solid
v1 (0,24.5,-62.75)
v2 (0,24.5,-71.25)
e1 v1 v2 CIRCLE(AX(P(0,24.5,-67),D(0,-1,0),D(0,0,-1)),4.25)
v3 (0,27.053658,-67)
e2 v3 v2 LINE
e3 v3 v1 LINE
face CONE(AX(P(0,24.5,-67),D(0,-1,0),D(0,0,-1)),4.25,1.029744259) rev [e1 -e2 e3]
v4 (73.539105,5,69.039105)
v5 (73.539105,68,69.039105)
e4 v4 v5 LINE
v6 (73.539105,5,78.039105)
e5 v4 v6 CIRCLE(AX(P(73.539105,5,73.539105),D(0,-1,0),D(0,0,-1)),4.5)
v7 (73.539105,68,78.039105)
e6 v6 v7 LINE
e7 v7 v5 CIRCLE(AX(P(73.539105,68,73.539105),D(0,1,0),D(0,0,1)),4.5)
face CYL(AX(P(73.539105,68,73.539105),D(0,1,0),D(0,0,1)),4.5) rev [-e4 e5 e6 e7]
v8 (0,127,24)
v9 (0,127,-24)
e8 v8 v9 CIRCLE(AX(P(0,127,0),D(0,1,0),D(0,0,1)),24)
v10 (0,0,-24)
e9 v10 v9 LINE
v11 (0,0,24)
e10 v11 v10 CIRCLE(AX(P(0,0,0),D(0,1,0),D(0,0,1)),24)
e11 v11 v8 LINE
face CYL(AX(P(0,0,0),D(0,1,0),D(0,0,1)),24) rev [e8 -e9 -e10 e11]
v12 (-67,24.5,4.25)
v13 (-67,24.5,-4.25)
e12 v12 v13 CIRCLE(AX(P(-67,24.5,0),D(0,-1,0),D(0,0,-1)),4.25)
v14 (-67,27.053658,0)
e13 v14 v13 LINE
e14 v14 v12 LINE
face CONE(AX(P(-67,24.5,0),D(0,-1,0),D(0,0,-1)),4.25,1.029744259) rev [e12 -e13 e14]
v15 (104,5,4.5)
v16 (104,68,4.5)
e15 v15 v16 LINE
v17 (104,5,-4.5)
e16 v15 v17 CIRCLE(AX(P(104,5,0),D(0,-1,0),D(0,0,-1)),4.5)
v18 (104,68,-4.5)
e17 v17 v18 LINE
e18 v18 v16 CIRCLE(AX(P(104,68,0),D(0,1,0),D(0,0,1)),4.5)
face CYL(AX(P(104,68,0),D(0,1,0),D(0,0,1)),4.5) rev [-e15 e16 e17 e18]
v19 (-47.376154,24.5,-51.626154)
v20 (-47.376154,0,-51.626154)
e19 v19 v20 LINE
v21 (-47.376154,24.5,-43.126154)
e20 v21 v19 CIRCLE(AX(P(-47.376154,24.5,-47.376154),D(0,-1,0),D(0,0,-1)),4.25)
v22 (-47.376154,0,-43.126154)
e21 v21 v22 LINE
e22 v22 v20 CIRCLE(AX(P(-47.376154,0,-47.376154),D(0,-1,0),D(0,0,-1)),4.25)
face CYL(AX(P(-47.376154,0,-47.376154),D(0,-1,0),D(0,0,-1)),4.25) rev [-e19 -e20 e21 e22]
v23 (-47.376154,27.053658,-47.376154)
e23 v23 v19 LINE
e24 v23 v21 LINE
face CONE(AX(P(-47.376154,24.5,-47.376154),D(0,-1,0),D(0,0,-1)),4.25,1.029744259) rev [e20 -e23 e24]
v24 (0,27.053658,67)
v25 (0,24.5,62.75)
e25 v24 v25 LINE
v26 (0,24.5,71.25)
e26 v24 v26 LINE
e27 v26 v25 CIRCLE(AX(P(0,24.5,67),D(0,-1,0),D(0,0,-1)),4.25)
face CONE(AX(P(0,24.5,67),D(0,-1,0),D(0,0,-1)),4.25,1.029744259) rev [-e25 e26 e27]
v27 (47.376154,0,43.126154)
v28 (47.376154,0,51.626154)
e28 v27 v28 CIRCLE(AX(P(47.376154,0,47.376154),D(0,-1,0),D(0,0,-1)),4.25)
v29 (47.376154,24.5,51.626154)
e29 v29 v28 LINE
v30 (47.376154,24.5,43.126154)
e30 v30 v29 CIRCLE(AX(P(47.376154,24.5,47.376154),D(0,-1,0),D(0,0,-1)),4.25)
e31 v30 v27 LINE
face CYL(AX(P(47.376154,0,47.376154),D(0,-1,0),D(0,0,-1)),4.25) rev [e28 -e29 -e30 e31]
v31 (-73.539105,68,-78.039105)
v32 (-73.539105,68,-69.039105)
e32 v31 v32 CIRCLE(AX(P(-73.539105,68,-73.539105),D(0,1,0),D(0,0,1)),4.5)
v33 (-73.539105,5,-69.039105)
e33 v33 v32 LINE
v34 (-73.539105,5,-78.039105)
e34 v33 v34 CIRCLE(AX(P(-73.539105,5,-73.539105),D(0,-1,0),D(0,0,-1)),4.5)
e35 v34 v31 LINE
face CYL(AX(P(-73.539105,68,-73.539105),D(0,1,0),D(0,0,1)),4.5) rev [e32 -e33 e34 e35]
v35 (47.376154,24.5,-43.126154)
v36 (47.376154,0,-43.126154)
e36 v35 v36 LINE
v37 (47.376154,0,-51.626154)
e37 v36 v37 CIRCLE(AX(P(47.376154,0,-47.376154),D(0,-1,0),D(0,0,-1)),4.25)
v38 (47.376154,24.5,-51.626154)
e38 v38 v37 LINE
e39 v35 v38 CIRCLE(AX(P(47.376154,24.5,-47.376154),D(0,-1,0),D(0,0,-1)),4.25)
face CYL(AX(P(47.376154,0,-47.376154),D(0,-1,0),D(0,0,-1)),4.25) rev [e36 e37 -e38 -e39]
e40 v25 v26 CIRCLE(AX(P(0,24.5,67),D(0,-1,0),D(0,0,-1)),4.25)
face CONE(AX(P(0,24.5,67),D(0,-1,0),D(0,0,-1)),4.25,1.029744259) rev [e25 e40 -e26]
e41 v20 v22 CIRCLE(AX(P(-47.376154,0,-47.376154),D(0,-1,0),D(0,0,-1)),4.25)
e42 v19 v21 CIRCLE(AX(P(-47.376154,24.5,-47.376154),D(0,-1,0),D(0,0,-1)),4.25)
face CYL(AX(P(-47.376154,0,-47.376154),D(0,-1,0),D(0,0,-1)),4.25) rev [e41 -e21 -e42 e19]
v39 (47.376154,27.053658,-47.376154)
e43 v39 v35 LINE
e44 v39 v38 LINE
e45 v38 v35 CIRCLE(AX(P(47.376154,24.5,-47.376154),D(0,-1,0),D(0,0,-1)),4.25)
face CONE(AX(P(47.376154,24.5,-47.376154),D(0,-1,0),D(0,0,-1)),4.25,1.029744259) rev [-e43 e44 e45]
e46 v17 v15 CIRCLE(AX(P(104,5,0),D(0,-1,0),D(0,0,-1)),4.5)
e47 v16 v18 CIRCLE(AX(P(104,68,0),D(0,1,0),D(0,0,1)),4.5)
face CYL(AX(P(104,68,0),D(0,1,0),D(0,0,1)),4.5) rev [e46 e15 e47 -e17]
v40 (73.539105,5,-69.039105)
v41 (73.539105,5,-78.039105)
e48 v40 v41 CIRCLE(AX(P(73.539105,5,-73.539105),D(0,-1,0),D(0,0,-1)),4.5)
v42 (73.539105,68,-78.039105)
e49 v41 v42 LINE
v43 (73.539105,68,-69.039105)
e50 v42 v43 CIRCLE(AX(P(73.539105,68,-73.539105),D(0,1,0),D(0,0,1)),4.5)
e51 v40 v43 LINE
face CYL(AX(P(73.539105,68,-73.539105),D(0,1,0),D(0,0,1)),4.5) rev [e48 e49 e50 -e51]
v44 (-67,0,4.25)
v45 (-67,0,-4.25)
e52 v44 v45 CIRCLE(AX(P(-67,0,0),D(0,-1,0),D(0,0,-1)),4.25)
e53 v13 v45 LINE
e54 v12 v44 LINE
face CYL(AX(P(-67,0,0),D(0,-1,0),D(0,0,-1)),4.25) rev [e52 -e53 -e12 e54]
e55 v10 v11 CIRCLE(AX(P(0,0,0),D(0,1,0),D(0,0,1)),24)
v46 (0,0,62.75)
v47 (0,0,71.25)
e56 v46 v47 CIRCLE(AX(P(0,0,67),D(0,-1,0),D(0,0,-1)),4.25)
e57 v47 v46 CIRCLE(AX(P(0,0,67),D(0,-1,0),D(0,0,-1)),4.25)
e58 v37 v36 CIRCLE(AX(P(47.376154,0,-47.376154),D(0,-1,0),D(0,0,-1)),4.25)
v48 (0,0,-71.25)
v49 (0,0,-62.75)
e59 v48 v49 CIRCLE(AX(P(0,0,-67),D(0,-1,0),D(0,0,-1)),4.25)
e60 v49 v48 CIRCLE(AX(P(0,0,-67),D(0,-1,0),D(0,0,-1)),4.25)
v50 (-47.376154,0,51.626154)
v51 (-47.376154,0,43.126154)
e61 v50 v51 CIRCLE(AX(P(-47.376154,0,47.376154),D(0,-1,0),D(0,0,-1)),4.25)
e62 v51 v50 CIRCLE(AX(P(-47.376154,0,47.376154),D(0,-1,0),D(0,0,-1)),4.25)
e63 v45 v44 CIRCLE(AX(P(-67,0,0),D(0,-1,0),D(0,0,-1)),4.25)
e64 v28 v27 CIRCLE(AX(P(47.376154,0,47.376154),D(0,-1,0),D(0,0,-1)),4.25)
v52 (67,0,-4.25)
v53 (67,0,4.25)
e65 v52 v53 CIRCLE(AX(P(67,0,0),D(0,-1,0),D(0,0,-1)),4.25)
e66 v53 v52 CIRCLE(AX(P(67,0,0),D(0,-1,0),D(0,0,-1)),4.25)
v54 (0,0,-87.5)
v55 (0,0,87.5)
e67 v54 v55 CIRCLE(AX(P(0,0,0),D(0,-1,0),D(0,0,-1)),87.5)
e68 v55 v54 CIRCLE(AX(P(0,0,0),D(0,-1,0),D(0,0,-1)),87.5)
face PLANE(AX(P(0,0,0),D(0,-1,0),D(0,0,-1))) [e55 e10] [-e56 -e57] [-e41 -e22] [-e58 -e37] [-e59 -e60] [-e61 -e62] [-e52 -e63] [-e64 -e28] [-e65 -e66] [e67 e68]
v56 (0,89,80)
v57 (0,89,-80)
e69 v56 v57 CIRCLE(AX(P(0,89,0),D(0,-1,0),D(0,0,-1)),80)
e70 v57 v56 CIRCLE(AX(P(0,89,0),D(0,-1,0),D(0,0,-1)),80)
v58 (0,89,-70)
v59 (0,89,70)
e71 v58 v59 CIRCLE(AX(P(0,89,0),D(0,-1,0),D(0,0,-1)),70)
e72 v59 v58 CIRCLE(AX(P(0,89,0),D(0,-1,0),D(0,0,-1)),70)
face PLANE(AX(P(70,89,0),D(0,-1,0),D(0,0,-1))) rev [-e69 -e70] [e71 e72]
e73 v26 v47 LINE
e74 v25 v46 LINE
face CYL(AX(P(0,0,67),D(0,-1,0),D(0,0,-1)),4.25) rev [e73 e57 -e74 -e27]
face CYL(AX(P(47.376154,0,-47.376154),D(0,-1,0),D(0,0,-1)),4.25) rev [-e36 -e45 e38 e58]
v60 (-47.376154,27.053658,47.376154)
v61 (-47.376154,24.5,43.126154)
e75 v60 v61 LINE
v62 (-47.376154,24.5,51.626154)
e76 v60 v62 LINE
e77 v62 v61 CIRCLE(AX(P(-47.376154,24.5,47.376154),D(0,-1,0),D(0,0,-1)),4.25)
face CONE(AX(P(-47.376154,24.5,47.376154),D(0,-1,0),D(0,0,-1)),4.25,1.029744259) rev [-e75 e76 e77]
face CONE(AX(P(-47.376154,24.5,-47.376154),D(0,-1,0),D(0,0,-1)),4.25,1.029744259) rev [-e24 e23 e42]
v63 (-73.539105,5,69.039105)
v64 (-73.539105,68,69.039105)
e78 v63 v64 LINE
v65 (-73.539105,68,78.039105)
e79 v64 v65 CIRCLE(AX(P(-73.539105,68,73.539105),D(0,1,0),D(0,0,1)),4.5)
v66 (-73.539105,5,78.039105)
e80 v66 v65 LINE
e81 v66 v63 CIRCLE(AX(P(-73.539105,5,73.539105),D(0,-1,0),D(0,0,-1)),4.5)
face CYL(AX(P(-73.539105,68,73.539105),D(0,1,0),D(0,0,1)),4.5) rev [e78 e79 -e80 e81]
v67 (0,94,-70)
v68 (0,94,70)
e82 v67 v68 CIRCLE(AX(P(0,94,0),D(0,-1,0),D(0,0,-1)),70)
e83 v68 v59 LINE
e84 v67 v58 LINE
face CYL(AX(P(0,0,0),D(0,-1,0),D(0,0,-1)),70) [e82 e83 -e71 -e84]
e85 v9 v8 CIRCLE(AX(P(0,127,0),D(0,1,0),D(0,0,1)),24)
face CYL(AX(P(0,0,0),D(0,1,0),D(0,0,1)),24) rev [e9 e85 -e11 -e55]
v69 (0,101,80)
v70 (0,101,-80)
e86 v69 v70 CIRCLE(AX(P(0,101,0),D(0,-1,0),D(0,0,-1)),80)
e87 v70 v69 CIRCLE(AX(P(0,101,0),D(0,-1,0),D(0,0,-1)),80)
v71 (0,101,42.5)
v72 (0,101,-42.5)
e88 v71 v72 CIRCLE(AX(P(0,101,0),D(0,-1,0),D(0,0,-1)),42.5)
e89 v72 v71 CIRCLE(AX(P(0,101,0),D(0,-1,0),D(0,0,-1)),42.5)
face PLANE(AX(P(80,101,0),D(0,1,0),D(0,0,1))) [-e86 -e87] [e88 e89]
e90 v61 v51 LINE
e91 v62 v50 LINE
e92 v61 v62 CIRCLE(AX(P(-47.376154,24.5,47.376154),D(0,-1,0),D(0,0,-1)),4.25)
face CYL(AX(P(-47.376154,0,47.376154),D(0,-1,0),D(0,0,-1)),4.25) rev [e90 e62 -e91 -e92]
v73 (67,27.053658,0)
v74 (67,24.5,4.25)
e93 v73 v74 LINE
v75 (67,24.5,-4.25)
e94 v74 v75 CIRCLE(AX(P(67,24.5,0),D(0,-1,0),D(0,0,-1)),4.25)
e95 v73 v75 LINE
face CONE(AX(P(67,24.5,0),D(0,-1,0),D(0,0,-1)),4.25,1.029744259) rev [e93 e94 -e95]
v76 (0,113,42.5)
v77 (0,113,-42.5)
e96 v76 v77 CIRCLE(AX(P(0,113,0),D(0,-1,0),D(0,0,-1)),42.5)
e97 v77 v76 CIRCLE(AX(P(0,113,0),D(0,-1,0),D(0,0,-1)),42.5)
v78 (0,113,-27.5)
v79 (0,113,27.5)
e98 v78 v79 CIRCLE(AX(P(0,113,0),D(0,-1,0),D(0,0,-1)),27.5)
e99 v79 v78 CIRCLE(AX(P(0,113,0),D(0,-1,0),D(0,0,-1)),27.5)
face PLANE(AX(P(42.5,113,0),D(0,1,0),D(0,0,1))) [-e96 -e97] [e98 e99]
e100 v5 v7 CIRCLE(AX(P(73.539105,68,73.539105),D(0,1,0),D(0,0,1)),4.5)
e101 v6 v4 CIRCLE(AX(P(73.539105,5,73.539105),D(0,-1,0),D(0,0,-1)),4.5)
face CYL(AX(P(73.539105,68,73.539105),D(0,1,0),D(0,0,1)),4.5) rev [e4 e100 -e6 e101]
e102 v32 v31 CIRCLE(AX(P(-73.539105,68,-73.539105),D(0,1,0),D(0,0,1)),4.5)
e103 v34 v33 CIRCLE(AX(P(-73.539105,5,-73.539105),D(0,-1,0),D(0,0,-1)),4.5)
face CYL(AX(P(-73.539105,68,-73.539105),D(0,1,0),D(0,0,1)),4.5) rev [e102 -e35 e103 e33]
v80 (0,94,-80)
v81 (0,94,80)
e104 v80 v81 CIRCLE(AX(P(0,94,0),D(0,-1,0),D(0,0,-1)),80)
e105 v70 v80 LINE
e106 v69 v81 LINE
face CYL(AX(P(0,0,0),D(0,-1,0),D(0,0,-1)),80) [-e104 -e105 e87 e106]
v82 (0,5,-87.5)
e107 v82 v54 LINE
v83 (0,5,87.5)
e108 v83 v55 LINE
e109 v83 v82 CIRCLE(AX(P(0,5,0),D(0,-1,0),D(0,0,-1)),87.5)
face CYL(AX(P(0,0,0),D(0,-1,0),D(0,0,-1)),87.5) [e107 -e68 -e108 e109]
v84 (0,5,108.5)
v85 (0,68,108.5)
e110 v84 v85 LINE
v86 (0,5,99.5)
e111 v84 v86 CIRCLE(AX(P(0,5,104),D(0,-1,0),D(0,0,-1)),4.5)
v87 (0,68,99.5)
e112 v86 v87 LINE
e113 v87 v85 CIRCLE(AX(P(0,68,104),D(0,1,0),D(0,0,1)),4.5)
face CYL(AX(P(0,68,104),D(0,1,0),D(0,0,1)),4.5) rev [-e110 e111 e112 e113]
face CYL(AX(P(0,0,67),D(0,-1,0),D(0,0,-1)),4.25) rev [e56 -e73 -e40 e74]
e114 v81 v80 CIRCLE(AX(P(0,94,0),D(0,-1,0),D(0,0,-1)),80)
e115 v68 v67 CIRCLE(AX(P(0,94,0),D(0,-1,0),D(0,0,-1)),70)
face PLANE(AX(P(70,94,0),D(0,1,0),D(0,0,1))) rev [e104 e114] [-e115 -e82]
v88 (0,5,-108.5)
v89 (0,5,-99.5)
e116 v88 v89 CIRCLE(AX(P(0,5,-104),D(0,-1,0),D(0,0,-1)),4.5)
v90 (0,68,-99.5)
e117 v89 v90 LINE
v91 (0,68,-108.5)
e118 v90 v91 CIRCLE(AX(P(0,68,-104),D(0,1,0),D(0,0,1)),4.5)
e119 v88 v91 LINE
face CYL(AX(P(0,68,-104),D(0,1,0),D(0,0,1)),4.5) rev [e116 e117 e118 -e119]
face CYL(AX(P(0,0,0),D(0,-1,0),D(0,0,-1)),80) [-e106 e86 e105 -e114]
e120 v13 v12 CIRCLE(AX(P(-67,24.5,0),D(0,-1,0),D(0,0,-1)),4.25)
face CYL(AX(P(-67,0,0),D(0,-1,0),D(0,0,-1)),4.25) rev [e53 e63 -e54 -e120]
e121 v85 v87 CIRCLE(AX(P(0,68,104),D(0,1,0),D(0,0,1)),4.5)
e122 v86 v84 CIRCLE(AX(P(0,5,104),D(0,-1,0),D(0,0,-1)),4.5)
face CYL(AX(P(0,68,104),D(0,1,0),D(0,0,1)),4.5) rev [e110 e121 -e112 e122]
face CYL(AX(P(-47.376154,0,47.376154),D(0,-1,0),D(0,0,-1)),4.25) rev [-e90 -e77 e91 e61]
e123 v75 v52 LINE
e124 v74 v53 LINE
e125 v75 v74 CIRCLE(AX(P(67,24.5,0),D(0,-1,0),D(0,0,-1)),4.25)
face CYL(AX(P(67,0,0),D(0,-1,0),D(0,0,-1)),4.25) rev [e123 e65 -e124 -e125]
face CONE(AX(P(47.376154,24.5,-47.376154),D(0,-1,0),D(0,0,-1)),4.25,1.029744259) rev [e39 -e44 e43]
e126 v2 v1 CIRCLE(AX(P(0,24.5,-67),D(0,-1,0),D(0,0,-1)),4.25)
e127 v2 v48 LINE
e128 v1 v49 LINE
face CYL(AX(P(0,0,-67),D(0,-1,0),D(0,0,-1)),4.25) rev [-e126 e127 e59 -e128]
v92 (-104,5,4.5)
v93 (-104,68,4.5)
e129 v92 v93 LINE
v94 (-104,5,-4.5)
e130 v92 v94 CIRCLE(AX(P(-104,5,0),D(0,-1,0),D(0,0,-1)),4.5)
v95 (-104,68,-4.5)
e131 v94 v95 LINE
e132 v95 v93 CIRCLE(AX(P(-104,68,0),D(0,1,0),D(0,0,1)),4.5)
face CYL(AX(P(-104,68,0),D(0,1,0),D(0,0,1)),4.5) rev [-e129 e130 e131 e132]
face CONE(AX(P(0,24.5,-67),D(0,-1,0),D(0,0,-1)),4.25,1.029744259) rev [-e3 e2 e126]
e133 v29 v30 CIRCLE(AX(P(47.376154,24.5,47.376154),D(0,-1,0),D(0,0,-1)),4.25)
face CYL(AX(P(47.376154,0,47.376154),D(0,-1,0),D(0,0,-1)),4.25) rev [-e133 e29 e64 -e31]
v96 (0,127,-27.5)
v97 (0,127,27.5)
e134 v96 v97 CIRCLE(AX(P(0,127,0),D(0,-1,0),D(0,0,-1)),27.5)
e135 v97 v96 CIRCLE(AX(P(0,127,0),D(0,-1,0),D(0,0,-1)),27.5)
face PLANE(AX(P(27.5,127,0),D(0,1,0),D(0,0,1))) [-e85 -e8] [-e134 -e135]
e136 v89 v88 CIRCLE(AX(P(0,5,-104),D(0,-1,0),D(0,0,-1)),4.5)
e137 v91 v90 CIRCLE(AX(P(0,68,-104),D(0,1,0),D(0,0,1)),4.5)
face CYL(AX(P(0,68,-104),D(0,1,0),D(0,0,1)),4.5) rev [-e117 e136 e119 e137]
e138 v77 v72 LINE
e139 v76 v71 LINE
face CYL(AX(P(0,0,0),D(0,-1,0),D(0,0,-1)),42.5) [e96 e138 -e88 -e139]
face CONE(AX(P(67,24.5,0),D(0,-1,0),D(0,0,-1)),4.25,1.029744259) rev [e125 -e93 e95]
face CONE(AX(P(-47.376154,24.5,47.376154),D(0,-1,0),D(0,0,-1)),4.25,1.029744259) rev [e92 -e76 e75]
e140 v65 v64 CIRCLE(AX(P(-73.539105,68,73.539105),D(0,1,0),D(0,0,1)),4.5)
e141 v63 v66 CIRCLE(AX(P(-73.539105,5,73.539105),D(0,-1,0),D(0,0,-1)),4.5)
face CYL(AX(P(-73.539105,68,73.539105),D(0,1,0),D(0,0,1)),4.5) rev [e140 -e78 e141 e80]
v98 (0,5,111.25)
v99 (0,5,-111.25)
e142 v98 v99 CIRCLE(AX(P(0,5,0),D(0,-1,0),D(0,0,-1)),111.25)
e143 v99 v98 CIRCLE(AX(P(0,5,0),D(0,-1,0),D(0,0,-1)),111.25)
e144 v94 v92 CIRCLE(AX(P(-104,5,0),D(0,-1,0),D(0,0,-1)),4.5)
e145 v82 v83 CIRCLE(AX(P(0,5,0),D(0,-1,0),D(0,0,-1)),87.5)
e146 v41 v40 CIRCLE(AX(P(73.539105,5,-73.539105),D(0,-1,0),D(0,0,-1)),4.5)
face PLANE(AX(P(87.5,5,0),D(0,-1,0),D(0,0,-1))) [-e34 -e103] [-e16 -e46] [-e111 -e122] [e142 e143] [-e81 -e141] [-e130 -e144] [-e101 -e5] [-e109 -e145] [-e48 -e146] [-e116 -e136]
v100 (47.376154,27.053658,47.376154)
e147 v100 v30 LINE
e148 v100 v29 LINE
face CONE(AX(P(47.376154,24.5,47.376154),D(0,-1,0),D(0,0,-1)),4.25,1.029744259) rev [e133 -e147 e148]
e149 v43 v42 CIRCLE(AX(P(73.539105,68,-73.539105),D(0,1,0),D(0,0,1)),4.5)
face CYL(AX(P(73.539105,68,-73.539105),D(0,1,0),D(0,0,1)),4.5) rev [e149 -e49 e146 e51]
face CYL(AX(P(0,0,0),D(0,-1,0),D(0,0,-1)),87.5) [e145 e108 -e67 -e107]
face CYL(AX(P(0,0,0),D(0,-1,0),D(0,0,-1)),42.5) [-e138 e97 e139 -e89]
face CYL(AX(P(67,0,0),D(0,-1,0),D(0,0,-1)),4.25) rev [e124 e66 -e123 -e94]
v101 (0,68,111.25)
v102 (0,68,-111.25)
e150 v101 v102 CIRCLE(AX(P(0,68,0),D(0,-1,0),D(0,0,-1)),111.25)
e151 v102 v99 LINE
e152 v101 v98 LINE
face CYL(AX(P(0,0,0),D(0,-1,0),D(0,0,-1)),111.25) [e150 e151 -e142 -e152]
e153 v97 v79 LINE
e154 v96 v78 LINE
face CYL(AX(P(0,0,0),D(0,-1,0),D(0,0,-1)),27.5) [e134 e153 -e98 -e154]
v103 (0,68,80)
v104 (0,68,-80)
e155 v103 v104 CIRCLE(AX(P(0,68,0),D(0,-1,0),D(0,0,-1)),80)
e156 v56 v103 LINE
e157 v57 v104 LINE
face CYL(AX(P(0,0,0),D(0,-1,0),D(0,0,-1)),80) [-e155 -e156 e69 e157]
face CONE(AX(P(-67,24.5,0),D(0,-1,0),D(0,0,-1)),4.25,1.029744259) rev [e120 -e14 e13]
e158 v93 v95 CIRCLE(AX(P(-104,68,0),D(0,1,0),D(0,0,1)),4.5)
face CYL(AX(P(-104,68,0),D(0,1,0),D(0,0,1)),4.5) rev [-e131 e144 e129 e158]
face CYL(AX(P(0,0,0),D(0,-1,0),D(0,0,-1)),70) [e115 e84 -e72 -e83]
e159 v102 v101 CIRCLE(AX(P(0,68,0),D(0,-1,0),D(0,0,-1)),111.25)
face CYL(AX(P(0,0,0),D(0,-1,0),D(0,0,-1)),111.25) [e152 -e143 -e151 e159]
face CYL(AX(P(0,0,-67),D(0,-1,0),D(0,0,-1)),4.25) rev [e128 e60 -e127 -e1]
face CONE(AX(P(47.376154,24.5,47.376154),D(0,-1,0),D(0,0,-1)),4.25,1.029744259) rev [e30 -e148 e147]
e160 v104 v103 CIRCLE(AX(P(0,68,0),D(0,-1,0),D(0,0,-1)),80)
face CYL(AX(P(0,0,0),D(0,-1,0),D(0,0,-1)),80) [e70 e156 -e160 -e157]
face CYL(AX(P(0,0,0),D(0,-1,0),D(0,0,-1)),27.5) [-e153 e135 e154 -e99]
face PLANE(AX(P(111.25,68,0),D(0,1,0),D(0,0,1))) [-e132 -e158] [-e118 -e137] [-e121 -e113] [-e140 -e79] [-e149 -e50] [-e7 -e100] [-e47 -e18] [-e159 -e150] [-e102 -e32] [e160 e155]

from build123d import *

# Parameters (mm, degrees)
SKETCH_2_R              = 24
CUT_EXTRUDE_1_DEPTH     = 203.193286239
HOLE_WIZARD_M8_1_D      = 9
SKETCH_7_W              = 10
SKETCH_7_H              = 5
HOLE_WIZARD_M10_1_D     = 8.5
HOLE_WIZARD_M10_1_DEPTH = 24.5
HOLE_WIZARD_M10_1_TIP   = 2.553657631


with BuildPart() as part:
    # 草图1 → 旋转1 (revolve)
    with BuildSketch(Plane.XY, mode=Mode.PRIVATE) as revolve_1_sk:
        Polygon((0, 0), (87.5, 0), (87.5, 5), (111.25, 5), (111.25, 68), (80, 68), (80, 101), (42.5, 101), (42.5, 113), (27.5, 113), (27.5, 127), (0, 127), align=None)
    revolve(revolve_1_sk.sketch.rotate(Axis((0, 0, 0), (0, 1, 0)), 90), axis=Axis((0, 0, 0), (0, 1, 0)))

    # 草图2 → 切除-拉伸1 (cut, through all)
    with BuildSketch(Plane(origin=(0, 127, 0), x_dir=(1, 0, 0), z_dir=(0, 1, 0))):
        with Locations(Location((0, 0, 0), (0, 0, 270))):
            Circle(SKETCH_2_R)
    extrude(amount=-CUT_EXTRUDE_1_DEPTH, mode=Mode.SUBTRACT)

    # M8 间隙孔1 (through all)
    with Locations(Plane(origin=(0, 68, 0), x_dir=(1, 0, 0), z_dir=(0, 1, 0))):
        with Locations((0, 104), (73.539105243, 73.539105243), (104, 0), (73.539105243, -73.539105243), (0, -104), (-73.539105243, -73.539105243), (-104, 0), (-73.539105243, 73.539105243)):
            Hole(HOLE_WIZARD_M8_1_D / 2)

    # 草图7 → 切除-旋转1 (revolve, cut)
    with BuildSketch(Plane.XY, mode=Mode.PRIVATE) as cut_revolve_1_sk:
        with Locations((75, 91.5)):
            Rectangle(SKETCH_7_W, SKETCH_7_H)
    revolve(cut_revolve_1_sk.sketch.rotate(Axis((0, 0, 0), (0, 1, 0)), 90), axis=Axis((0, 0, 0), (0, 1, 0)), mode=Mode.SUBTRACT)

    # M10 螺纹孔1
    with Locations(Plane(origin=(0, 0, 0), x_dir=(-1, 0, 0), z_dir=(0, -1, 0))):
        with Locations((0, 67), (47.376154339, 47.376154339), (67, 0), (47.376154339, -47.376154339), (0, -67), (-47.376154339, -47.376154339), (-67, 0), (-47.376154339, 47.376154339)):
            Hole(HOLE_WIZARD_M10_1_D / 2, depth=HOLE_WIZARD_M10_1_DEPTH)
            with Locations((0, 0, -(HOLE_WIZARD_M10_1_DEPTH + HOLE_WIZARD_M10_1_TIP / 2))):  # 118° drill point
                Cone(0, HOLE_WIZARD_M10_1_D / 2, HOLE_WIZARD_M10_1_TIP, mode=Mode.SUBTRACT)


solid = part.part
